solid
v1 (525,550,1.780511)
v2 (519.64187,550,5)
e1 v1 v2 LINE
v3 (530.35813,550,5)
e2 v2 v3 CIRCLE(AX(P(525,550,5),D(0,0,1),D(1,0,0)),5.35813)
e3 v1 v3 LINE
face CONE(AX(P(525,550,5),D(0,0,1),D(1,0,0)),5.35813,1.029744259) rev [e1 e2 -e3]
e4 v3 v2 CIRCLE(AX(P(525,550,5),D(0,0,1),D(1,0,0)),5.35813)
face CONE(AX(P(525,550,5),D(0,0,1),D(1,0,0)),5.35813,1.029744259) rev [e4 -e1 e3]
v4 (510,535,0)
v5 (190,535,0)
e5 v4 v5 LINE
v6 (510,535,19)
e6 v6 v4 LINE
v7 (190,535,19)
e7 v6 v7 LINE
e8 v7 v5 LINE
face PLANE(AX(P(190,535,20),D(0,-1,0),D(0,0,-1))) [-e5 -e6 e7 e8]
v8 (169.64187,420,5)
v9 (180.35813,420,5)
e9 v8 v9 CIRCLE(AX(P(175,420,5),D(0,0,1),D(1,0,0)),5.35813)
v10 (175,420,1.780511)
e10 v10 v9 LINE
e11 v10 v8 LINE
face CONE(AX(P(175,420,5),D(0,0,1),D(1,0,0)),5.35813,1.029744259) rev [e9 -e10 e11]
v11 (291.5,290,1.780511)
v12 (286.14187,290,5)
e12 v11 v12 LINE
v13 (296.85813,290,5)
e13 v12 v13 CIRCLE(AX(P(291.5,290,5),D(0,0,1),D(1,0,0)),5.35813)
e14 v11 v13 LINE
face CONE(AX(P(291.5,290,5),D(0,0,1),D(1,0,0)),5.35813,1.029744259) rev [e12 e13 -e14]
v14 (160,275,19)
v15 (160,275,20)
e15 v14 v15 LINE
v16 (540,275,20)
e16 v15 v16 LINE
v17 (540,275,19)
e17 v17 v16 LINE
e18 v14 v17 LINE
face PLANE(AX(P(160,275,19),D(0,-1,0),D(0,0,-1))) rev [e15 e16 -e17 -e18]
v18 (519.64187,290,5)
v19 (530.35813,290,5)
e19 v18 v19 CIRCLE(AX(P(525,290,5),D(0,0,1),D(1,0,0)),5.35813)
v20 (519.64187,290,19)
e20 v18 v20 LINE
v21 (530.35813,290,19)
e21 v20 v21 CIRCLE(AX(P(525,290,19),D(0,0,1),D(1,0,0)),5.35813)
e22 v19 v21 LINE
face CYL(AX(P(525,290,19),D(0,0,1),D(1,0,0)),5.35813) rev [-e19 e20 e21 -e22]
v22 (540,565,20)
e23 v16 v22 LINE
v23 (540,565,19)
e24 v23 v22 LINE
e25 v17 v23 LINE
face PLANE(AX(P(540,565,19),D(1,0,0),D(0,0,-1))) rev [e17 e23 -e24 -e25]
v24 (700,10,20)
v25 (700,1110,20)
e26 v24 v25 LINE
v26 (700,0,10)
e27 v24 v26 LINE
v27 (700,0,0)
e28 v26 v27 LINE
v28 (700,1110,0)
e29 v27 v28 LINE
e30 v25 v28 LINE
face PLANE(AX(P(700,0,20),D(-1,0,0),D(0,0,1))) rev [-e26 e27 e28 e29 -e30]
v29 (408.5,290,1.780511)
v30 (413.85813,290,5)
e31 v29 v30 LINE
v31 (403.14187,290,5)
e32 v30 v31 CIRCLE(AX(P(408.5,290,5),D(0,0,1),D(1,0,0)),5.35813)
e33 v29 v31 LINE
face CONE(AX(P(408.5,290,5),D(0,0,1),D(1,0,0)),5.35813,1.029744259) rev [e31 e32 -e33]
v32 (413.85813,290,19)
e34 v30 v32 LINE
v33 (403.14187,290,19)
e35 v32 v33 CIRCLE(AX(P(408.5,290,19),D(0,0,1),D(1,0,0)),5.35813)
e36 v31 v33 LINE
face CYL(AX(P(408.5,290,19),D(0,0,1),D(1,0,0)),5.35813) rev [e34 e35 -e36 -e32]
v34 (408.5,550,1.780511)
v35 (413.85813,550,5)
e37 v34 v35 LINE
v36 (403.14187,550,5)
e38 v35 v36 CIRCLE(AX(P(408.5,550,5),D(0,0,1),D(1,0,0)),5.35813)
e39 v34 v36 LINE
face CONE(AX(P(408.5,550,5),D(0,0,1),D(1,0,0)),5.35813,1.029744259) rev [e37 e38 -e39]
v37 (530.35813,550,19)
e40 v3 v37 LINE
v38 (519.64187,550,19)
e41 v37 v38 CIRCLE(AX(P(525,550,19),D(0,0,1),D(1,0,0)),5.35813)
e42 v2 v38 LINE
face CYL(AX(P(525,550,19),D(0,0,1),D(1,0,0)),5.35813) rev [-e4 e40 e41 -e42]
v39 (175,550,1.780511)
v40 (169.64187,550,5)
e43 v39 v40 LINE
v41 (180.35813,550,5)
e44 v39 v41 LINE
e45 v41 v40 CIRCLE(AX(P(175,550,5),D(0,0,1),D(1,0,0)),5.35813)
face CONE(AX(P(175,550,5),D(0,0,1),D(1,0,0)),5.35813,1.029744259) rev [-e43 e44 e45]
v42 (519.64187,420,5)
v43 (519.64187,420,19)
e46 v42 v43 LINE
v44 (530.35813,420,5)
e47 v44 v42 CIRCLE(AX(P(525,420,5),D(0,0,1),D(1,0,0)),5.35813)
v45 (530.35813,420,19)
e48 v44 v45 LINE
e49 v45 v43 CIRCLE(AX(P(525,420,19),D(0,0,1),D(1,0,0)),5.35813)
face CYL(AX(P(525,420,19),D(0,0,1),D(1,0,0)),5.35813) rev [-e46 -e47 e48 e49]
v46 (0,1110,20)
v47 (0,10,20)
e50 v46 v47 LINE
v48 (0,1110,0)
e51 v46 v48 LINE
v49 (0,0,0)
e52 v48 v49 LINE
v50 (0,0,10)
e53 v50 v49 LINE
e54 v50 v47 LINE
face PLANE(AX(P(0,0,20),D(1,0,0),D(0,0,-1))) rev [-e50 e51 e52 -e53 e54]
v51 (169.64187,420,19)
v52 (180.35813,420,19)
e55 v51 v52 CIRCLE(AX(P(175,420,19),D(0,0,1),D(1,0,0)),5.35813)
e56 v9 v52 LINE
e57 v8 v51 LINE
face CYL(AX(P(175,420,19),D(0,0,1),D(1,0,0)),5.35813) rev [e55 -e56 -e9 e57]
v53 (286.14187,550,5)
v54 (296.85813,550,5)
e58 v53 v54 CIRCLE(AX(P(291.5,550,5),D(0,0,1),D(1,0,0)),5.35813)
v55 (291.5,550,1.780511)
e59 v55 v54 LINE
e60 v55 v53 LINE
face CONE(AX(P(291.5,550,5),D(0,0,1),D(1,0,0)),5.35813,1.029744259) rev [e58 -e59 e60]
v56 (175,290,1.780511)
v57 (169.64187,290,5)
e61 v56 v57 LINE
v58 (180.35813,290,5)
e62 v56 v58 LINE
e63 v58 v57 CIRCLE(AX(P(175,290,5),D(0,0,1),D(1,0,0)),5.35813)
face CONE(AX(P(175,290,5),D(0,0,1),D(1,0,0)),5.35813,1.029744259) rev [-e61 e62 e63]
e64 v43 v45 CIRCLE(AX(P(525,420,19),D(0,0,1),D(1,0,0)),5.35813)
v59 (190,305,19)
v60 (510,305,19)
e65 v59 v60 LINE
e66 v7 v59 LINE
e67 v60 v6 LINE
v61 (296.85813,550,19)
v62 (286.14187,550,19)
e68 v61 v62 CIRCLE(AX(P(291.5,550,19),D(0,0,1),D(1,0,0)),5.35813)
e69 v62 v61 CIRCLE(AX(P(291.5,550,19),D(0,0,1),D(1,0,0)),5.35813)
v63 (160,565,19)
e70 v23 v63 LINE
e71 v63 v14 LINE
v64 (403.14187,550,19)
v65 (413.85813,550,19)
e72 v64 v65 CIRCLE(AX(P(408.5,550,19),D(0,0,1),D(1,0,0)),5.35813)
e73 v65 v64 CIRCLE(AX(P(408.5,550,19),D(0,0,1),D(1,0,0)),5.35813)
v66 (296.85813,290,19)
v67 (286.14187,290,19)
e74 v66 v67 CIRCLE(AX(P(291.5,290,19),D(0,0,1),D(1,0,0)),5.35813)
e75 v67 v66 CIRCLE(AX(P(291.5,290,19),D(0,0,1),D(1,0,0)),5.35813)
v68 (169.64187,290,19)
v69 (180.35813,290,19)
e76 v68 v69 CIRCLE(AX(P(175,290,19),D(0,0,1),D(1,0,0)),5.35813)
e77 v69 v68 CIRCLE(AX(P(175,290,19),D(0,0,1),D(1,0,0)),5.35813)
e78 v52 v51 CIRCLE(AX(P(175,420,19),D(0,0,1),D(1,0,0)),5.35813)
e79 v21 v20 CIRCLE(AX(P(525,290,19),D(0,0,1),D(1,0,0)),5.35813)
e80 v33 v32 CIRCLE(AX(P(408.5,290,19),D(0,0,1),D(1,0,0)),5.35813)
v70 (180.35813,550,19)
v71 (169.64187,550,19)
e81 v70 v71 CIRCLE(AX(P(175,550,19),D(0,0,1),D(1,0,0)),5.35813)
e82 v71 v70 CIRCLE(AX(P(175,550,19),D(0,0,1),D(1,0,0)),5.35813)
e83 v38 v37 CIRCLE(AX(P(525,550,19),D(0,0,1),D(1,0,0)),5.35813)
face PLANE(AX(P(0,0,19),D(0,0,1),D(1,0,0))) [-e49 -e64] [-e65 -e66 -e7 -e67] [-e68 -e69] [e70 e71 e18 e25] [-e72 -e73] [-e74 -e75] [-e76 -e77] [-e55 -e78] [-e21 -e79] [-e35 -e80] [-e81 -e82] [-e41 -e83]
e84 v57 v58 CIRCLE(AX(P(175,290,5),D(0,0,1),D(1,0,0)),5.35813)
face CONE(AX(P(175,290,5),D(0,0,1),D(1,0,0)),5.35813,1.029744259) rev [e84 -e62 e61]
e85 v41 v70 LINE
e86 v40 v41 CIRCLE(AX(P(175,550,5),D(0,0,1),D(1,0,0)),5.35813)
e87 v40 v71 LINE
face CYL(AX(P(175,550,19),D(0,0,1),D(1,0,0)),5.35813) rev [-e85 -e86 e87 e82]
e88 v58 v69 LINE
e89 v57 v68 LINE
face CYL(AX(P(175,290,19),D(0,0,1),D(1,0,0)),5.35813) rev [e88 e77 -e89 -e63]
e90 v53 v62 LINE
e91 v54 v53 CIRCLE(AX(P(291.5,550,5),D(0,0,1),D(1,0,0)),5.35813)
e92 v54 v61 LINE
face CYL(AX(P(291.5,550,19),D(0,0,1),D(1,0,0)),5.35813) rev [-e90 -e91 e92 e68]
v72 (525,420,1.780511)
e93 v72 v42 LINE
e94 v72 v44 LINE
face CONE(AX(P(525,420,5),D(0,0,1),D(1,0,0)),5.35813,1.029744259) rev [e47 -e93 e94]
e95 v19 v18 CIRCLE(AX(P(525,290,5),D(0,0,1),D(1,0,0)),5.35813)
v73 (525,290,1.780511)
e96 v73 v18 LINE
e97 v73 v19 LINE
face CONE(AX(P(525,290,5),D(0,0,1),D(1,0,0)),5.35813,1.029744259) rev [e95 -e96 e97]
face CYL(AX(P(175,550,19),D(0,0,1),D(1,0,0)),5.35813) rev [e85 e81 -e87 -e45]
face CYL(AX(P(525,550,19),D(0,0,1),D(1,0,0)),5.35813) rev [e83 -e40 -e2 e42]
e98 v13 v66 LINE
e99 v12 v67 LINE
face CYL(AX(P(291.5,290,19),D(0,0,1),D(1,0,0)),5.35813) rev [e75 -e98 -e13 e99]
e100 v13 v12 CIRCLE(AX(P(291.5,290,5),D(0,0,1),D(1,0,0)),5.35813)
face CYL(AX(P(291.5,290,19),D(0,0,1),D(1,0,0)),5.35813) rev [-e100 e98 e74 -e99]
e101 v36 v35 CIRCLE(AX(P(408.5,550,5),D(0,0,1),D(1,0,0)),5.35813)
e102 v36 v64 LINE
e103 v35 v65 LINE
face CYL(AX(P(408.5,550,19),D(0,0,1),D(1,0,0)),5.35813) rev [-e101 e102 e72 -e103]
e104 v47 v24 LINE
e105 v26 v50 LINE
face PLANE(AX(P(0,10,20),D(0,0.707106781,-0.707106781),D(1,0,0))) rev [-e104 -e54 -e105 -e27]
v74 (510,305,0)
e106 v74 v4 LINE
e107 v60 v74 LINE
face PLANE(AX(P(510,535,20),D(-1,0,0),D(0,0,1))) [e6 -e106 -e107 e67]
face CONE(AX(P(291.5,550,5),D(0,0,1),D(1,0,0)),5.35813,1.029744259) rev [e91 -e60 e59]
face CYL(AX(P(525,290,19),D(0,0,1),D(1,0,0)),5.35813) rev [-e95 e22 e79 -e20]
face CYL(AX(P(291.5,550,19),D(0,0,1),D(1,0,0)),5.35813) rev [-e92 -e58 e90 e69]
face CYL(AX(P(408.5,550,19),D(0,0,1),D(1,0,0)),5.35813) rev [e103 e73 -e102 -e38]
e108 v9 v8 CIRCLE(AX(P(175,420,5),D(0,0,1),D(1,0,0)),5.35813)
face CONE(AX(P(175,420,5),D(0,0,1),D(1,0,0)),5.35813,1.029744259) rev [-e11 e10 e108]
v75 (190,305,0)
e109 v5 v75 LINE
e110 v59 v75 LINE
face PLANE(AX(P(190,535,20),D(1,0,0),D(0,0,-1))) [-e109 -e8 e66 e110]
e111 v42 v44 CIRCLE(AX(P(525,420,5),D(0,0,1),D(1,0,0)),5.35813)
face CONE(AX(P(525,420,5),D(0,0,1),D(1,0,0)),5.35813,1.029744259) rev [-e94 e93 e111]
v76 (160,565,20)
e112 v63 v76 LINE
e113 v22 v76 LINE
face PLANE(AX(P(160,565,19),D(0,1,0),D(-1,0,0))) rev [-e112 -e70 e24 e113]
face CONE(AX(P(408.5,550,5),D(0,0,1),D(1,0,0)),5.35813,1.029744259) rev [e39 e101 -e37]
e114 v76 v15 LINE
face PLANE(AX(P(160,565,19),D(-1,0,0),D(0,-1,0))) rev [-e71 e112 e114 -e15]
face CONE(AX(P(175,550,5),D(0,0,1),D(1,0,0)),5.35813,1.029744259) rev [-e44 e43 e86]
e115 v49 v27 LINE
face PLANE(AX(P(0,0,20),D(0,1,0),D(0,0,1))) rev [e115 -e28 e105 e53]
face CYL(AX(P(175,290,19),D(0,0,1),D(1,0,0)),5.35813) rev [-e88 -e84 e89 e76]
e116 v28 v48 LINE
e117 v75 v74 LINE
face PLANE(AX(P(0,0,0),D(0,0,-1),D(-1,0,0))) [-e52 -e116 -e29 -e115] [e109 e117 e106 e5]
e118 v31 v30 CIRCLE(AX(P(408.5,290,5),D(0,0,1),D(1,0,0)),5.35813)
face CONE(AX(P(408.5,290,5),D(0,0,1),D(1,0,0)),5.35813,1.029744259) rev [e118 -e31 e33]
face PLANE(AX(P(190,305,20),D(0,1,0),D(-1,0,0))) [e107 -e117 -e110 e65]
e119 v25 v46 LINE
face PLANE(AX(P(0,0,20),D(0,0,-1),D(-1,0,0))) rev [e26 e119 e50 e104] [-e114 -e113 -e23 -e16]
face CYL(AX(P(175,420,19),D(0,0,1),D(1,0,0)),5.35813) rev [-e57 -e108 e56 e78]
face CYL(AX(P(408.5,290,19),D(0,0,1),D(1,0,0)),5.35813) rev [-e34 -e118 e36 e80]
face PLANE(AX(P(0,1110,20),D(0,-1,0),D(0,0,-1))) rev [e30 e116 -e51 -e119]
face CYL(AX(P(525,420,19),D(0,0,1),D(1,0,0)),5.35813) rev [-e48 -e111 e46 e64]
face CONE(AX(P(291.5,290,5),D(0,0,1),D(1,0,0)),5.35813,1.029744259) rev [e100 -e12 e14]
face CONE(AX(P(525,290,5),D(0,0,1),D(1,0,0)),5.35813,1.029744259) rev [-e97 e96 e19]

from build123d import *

# Parameters (mm, degrees)
SKETCH1_W                     = 700
SKETCH1_H                     = 1110
SKETCH1_W_2                   = 320
SKETCH1_H_2                   = 230
BOSS_EXTRUDE1_DEPTH           = 20
SKETCH2_W                     = 380
SKETCH2_H                     = 290
CUT_EXTRUDE1_DEPTH            = 1
F_1_2_13_THREADED_HOLE1_D     = 10.71626
F_1_2_13_THREADED_HOLE1_DEPTH = 14
F_1_2_13_THREADED_HOLE1_TIP   = 3.219489309
CHAMFER1_SIZE                 = 10


with BuildPart() as part:
    # Sketch1 → Boss-Extrude1 (new body)
    with BuildSketch(Plane.XY):
        with Locations((350, 555)):
            Rectangle(SKETCH1_W, SKETCH1_H)
        with Locations((350, 420)):
            Rectangle(SKETCH1_W_2, SKETCH1_H_2, mode=Mode.SUBTRACT)
    extrude(amount=BOSS_EXTRUDE1_DEPTH)

    # Sketch2 → Cut-Extrude1 (cut)
    with BuildSketch(Plane.XY.offset(20)):
        with Locations((350, 420)):
            Rectangle(SKETCH2_W, SKETCH2_H)
    extrude(amount=-CUT_EXTRUDE1_DEPTH, mode=Mode.SUBTRACT)

    # 1/2-13 Threaded hole1
    with Locations(Plane(origin=(175, 550, 19), x_dir=(1, 0, 0), z_dir=(0, 0, 1))):
        with Locations((0, 0), (116.5, 0), (233.5, 0), (350, 0), (350, -130), (350, -260), (233.5, -260), (116.5, -260), (0, -260), (0, -130)):
            Hole(F_1_2_13_THREADED_HOLE1_D / 2, depth=F_1_2_13_THREADED_HOLE1_DEPTH)
            with Locations((0, 0, -(F_1_2_13_THREADED_HOLE1_DEPTH + F_1_2_13_THREADED_HOLE1_TIP / 2))):  # 118° drill point
                Cone(0, F_1_2_13_THREADED_HOLE1_D / 2, F_1_2_13_THREADED_HOLE1_TIP, mode=Mode.SUBTRACT)

    # Chamfer1
    chamfer1_edges = [part.edges().sort_by_distance(p)[0] for p in [
        (350, 0, 20),
    ]]
    chamfer(chamfer1_edges, length=CHAMFER1_SIZE)


solid = part.part
